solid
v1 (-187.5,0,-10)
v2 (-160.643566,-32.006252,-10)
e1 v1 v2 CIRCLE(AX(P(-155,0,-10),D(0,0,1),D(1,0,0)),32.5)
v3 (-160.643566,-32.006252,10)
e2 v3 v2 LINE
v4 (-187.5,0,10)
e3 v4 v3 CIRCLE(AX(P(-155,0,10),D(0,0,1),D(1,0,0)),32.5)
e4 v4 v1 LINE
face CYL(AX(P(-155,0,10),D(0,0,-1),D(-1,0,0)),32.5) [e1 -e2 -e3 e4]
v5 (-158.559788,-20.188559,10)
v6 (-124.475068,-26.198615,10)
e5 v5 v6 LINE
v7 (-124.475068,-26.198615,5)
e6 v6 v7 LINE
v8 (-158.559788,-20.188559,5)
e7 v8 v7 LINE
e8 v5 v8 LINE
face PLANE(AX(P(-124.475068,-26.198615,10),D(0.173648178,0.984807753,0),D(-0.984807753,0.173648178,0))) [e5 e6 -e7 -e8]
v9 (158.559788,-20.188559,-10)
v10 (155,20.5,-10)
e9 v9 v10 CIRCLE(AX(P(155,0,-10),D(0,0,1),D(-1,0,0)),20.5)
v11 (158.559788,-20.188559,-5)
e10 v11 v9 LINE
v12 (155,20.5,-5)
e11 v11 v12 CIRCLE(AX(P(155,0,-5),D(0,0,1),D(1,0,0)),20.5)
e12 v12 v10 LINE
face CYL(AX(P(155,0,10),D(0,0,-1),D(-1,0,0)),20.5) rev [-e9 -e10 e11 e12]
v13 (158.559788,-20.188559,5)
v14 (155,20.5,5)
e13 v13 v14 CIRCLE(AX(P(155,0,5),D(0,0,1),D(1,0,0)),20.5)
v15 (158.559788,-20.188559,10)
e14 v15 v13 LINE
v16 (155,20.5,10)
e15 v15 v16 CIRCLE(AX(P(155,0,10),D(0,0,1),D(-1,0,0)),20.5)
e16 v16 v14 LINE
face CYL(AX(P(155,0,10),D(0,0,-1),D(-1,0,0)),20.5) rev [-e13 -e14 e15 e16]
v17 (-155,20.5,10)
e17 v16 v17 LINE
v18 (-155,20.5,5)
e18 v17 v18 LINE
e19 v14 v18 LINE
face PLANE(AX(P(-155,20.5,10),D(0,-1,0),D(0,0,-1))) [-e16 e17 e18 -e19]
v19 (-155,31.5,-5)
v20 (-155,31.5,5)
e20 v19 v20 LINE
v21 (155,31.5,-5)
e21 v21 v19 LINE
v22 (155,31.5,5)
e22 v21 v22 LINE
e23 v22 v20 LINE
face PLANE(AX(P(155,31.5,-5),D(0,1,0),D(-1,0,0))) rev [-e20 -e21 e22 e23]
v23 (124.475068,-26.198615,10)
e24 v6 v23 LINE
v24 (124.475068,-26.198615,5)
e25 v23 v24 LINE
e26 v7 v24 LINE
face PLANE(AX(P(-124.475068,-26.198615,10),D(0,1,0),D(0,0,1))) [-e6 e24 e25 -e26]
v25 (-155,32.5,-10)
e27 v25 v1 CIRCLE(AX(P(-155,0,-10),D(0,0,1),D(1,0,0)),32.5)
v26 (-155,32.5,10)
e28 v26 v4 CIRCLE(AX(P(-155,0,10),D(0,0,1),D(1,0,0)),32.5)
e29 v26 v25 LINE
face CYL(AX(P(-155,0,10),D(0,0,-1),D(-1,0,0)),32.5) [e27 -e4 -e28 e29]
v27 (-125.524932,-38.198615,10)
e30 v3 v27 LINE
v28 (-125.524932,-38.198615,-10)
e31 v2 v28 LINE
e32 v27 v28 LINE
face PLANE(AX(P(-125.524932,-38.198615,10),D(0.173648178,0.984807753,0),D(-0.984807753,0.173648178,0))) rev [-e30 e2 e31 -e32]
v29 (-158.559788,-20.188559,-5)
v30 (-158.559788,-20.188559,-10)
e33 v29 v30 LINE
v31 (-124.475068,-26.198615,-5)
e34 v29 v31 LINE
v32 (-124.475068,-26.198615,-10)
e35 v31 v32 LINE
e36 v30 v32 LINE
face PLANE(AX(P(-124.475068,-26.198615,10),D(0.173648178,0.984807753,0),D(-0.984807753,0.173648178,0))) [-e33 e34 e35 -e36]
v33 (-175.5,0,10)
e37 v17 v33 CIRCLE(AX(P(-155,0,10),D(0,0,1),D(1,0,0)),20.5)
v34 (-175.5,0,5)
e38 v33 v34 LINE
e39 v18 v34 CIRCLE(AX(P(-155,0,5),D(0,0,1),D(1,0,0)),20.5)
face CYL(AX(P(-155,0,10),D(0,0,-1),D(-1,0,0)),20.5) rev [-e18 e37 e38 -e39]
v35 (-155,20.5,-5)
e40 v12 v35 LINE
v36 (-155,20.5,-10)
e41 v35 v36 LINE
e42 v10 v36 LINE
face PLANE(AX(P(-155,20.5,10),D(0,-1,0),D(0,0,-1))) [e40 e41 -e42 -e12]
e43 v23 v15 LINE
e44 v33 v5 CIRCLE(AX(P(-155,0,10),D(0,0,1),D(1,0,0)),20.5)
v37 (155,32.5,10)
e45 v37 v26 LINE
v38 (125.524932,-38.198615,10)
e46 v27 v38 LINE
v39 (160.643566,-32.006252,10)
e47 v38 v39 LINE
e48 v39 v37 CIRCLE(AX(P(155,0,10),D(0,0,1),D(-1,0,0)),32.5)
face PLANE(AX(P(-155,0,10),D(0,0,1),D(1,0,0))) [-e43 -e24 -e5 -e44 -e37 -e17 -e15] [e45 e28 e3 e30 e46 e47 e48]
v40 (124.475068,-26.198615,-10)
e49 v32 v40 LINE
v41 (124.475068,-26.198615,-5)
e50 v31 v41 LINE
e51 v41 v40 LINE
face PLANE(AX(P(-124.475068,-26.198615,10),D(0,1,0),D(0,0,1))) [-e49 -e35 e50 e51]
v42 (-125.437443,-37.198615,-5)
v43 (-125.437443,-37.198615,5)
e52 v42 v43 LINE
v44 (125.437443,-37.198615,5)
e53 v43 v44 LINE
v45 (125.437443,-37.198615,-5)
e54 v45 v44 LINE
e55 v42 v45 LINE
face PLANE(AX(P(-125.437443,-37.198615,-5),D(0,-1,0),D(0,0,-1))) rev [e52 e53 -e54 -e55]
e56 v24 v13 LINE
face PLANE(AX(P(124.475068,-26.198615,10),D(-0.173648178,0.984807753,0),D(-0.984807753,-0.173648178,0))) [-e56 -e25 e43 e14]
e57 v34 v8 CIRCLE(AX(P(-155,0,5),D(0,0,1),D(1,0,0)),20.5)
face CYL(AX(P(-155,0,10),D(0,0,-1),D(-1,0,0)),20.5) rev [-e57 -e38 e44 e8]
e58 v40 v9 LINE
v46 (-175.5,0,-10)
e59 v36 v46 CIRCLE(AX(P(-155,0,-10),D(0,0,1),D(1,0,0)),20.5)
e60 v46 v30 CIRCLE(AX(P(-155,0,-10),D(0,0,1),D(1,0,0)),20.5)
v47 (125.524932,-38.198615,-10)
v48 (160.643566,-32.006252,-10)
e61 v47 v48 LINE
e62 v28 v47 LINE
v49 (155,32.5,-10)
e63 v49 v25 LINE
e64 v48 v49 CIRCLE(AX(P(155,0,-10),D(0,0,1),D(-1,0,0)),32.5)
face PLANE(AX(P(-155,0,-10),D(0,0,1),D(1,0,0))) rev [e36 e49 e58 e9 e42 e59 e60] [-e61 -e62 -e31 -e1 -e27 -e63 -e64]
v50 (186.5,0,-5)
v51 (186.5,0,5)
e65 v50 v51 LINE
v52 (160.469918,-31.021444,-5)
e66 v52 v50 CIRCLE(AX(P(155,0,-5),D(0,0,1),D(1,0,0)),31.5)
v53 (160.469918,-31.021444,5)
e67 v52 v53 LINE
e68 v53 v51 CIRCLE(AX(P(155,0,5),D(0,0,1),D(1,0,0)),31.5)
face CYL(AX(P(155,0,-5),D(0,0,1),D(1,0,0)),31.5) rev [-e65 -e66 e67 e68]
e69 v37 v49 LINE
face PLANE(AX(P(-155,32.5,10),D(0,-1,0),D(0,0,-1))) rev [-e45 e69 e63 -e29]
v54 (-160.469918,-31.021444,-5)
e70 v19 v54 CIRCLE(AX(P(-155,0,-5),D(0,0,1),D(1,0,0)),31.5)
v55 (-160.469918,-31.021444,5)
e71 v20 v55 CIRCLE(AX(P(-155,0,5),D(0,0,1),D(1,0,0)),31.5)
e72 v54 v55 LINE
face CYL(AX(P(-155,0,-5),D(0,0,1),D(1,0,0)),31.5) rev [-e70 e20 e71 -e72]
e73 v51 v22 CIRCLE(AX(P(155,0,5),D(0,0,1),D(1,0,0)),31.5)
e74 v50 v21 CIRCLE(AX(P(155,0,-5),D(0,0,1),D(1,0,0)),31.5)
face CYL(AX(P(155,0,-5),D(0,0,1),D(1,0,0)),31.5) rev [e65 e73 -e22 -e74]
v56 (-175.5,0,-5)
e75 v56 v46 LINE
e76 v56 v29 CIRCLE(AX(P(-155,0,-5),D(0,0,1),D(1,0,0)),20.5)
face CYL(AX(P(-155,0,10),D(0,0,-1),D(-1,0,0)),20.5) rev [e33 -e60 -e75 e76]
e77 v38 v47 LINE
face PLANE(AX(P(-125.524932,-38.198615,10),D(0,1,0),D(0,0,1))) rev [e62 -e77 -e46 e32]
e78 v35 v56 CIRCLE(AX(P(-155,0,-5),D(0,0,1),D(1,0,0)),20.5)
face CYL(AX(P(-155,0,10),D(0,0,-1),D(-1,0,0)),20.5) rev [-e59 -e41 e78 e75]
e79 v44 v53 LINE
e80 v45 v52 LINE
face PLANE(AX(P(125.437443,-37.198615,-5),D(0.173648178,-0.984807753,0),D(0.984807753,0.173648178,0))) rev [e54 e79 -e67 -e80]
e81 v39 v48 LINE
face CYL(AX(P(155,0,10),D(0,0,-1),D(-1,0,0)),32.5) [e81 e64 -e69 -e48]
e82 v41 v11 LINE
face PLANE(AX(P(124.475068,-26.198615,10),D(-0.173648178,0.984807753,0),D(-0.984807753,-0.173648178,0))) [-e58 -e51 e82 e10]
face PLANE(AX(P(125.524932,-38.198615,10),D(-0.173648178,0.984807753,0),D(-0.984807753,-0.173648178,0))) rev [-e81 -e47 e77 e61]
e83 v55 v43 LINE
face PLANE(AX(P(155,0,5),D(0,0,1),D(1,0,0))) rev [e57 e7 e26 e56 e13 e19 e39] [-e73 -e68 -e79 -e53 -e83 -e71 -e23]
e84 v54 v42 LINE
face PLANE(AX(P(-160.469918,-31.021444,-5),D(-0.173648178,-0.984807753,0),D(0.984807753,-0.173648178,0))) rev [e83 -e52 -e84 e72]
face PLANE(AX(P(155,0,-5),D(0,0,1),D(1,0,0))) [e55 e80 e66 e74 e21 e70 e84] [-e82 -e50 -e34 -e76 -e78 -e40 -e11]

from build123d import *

# Parameters (mm, degrees)
BOSS_EXTRUDE1_DEPTH = 10
CUT_EXTRUDE1_DEPTH  = 5


with BuildPart() as part:
    # Sketch2 → Boss-Extrude1 (new, symmetric)
    with BuildSketch(Plane.XY):
        with BuildLine():
            Line((-155, 32.5), (155, 32.5))
            ThreePointArc((155, 32.5), (187.376327688, 2.832561639), (160.643565774, -32.006251973))
            Line((160.643565774, -32.006251973), (125.524931981, -38.198614636))
            Line((125.524931981, -38.198614636), (-125.524931981, -38.198614636))
            Line((-125.524931981, -38.198614636), (-160.643565774, -32.006251973))
            ThreePointArc((-160.643565774, -32.006251973), (-187.376327688, 2.832561639), (-155, 32.5))
        make_face()
        with BuildLine():
            Line((-155, 20.5), (155, 20.5))
            ThreePointArc((155, 20.5), (175.421991311, 1.786692726), (158.559787642, -20.188558937))
            Line((158.559787642, -20.188558937), (124.475068019, -26.198614636))
            Line((124.475068019, -26.198614636), (-124.475068019, -26.198614636))
            Line((-124.475068019, -26.198614636), (-158.559787642, -20.188558937))
            ThreePointArc((-158.559787642, -20.188558937), (-175.421991311, 1.786692726), (-155, 20.5))
        make_face(mode=Mode.SUBTRACT)
    extrude(amount=BOSS_EXTRUDE1_DEPTH, both=True)

    # Sketch8 → Cut-Extrude1 (cut, symmetric)
    with BuildSketch(Plane.XY):
        with BuildLine():
            Line((125.437443318, -37.198614636), (160.469917597, -31.02144422))
            ThreePointArc((160.469917597, -31.02144422), (186.38013299, 2.745405897), (155, 31.5))
            Line((155, 31.5), (-155, 31.5))
            ThreePointArc((-155, 31.5), (-186.38013299, 2.745405897), (-160.469917597, -31.02144422))
            Line((-160.469917597, -31.02144422), (-125.437443318, -37.198614636))
            Line((-125.437443318, -37.198614636), (125.437443318, -37.198614636))
        make_face()
    extrude(amount=CUT_EXTRUDE1_DEPTH, both=True, mode=Mode.SUBTRACT)


solid = part.part
